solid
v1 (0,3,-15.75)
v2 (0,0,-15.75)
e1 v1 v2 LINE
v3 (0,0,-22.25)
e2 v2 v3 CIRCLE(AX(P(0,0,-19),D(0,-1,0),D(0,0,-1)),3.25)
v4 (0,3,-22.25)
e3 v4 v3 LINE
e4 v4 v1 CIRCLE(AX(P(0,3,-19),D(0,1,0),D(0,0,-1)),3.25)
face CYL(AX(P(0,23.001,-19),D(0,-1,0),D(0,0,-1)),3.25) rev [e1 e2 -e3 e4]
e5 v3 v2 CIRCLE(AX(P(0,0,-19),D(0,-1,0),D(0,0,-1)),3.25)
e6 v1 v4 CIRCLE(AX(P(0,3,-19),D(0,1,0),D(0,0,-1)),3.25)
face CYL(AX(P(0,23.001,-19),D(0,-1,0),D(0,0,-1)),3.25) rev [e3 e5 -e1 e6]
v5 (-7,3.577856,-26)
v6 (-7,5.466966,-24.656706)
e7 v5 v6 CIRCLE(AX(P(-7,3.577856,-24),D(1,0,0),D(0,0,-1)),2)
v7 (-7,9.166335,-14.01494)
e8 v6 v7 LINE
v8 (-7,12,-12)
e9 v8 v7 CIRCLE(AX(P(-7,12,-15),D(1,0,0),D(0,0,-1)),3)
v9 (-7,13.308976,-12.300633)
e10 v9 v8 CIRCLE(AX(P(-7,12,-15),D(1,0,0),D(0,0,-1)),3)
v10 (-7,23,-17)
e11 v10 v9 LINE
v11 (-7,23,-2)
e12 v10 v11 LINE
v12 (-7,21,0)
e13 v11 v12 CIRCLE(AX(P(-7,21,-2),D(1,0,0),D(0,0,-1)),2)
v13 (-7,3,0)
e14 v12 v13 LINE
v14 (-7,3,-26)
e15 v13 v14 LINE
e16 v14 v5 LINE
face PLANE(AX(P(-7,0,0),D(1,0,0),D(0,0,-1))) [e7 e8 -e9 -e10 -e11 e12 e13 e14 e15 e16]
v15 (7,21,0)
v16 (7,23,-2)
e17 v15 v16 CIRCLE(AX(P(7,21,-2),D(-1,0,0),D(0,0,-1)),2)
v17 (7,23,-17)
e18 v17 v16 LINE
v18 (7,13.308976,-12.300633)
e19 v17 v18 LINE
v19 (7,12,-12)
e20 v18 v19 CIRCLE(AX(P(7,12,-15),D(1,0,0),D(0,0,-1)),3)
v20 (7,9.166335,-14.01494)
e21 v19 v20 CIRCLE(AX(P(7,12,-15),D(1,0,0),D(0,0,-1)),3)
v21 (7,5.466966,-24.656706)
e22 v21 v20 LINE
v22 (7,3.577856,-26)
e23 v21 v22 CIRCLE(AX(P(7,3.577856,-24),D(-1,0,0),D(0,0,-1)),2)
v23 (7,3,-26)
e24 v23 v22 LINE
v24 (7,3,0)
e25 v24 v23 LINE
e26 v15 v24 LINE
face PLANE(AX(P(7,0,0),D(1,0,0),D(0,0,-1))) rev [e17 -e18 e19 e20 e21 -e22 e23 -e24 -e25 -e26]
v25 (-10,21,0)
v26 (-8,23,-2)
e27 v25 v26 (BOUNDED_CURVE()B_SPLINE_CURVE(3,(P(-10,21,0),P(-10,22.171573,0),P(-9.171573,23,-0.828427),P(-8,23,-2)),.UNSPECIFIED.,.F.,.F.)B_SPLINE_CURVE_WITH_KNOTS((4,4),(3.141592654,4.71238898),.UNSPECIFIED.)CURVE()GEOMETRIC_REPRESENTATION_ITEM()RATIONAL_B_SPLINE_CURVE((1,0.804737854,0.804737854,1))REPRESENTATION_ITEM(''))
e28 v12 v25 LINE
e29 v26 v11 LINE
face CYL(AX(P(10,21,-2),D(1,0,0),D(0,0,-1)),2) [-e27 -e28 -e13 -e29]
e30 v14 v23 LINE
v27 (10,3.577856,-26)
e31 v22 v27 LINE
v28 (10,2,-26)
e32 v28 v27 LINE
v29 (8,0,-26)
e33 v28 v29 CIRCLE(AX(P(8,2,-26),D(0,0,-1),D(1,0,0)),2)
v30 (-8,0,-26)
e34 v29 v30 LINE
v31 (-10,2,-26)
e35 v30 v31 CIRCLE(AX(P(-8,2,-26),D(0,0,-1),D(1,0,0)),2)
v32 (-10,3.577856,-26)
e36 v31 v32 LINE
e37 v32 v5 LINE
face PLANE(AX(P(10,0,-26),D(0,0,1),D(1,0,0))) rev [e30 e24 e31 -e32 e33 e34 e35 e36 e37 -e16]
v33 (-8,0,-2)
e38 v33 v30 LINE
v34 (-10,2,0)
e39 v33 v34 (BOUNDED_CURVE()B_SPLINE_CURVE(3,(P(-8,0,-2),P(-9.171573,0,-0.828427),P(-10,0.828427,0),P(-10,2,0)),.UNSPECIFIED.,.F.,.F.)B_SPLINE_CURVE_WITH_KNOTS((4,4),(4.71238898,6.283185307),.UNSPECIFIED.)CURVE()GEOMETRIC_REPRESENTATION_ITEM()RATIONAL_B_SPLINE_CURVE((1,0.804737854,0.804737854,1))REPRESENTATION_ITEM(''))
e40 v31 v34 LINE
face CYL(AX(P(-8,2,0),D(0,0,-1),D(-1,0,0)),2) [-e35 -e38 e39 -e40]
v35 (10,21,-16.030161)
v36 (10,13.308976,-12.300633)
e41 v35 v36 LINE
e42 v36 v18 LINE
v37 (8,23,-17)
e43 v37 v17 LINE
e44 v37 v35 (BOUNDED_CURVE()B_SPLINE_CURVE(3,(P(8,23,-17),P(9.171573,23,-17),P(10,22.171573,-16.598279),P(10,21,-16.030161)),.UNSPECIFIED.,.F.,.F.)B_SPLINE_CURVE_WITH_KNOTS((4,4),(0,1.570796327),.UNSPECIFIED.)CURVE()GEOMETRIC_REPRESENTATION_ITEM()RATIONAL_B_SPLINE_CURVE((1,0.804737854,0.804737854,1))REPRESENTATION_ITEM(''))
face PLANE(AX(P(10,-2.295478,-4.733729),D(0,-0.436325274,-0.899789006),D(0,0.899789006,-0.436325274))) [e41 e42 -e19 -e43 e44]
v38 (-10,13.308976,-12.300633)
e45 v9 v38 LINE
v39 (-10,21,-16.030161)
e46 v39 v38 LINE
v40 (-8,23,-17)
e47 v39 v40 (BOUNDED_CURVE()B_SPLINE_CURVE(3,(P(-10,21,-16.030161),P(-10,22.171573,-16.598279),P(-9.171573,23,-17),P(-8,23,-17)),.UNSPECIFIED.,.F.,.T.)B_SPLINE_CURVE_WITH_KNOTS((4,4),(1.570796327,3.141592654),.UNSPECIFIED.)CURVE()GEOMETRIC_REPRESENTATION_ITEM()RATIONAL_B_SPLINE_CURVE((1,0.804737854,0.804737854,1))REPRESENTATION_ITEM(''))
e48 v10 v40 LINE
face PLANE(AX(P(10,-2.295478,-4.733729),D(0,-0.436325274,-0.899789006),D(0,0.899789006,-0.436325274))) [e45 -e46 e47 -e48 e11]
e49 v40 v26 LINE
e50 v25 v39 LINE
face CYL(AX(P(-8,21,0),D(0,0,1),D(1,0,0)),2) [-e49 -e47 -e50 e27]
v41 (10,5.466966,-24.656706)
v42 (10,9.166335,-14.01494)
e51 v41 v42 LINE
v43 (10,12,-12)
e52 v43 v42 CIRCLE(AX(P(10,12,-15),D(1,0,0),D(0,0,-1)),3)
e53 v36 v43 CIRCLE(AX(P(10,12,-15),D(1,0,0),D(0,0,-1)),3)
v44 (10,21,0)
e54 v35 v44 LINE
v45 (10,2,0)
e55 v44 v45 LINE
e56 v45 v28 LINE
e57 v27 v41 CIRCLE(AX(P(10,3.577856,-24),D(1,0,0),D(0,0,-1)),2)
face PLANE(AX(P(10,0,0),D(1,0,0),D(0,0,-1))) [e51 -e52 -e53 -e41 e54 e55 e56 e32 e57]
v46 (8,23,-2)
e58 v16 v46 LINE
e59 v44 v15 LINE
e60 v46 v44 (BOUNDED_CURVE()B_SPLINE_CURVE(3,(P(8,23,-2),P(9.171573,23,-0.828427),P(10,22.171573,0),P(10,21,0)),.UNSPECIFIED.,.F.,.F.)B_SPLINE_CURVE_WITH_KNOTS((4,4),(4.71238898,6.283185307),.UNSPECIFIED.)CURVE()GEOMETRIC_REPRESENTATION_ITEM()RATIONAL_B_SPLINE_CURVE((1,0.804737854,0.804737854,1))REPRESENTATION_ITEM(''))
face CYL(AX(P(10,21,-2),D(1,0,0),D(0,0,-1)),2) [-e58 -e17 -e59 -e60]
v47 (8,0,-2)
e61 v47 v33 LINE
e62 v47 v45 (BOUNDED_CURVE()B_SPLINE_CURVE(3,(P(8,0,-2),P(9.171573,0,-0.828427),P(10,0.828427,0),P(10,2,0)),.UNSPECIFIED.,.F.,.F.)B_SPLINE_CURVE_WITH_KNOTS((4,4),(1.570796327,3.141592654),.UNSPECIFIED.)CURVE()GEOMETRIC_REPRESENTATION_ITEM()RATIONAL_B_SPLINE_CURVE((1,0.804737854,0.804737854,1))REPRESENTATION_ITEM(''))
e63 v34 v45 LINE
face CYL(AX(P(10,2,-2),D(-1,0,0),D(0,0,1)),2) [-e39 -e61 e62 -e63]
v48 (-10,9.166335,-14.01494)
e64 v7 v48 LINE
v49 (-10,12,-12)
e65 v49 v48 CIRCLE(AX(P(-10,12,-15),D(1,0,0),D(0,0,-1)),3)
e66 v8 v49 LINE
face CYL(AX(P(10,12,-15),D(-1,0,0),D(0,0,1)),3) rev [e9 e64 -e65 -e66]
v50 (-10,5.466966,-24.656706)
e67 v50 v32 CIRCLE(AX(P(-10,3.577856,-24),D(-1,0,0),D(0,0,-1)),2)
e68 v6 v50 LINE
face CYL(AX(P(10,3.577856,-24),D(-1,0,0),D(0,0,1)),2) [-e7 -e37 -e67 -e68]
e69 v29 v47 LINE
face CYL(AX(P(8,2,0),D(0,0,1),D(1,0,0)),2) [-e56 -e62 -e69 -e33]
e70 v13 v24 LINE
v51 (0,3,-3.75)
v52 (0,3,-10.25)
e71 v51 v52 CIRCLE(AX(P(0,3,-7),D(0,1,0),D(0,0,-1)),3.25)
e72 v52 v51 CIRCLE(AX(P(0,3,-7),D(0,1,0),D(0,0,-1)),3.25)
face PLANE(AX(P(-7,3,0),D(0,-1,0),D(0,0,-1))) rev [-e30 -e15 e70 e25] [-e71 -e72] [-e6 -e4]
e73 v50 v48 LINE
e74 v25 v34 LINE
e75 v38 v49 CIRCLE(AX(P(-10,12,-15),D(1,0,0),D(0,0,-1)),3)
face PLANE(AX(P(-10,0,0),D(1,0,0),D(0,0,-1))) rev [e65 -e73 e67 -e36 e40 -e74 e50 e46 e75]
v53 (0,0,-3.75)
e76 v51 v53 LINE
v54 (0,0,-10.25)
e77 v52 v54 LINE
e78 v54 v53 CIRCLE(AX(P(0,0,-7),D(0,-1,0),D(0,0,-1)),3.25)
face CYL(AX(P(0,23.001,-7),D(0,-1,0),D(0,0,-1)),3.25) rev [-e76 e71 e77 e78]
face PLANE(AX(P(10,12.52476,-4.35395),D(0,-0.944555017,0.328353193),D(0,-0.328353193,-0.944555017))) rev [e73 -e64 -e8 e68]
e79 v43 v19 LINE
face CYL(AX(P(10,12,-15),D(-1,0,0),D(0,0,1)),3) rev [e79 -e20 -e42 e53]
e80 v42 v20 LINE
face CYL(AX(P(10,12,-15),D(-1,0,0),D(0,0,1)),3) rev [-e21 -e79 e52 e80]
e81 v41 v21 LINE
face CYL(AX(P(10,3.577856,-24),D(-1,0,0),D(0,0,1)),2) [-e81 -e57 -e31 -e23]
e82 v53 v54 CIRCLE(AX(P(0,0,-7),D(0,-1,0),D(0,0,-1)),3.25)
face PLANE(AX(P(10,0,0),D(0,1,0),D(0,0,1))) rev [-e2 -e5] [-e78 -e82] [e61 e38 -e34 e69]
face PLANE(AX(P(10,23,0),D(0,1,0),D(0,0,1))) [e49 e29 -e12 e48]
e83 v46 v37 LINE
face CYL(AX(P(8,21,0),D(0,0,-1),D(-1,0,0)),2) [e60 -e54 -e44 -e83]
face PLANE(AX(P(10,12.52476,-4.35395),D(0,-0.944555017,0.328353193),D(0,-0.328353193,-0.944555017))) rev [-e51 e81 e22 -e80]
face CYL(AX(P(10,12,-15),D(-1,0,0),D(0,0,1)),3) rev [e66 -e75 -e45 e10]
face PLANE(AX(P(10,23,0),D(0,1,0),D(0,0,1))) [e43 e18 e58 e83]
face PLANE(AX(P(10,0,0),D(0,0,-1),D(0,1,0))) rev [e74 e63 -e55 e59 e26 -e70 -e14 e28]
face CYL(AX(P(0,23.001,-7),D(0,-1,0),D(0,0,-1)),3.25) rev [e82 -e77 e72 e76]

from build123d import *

# Parameters (mm, degrees)
EXTRUDE_1_DEPTH     = 10
SKETCH_2_W          = 26
SKETCH_2_H          = 20
CUT_EXTRUDE_1_DEPTH = 7
CUT_EXTRUDE_2_REACH = 38.125
SKETCH_3_R          = 3.25
FILLET_3_R          = 2


with BuildPart() as part:
    # 草图1 → 凸台-拉伸1 (new, symmetric)
    with BuildSketch(Plane(origin=(0, 0, 0), x_dir=(0, 0, -1), z_dir=(1, 0, 0))):
        with BuildLine():
            Line((17, 23), (0, 23))
            Line((0, 23), (0, 0))
            Line((0, 0), (26, 0))
            Line((26, 0), (26, 5))
            Line((26, 5), (14.014940421, 9.166334948))
            ThreePointArc((14.014940421, 9.166334948), (12.227975796, 10.852881082), (12.300632982, 13.308975821))
            Line((12.300632982, 13.308975821), (17, 23))
        make_face()
    extrude(amount=EXTRUDE_1_DEPTH, both=True)

    # 草图2 → 切除-拉伸1 (cut, symmetric)
    with BuildSketch(Plane(origin=(0, 0, 0), x_dir=(0, 0, -1), z_dir=(1, 0, 0))):
        with Locations((13, 13)):
            Rectangle(SKETCH_2_W, SKETCH_2_H)
    extrude(amount=CUT_EXTRUDE_1_DEPTH, both=True, mode=Mode.SUBTRACT)

    # 草图3 → 切除-拉伸2 (cut, up to next)
    with BuildSketch(Plane.XZ, mode=Mode.PRIVATE) as cut_extrude_2_sk1:
        with Locations(Location((0, -7, 0), (0, 0, 270))):
            Circle(SKETCH_3_R)
    cut_extrude_2_tool1 = extrude(cut_extrude_2_sk1.sketch, amount=-CUT_EXTRUDE_2_REACH, mode=Mode.PRIVATE) & part.part
    # 草图3 → 切除-拉伸2 (cut, up to next)
    with BuildSketch(Plane.XZ, mode=Mode.PRIVATE) as cut_extrude_2_sk2:
        with Locations(Location((0, -19, 0), (0, 0, 270))):
            Circle(SKETCH_3_R)
    cut_extrude_2_tool2 = extrude(cut_extrude_2_sk2.sketch, amount=-CUT_EXTRUDE_2_REACH, mode=Mode.PRIVATE) & part.part
    add(cut_extrude_2_tool1.solids().sort_by_distance((0, 0, -7))[0], mode=Mode.SUBTRACT)
    add(cut_extrude_2_tool2.solids().sort_by_distance((0, 0, -19))[0], mode=Mode.SUBTRACT)

    # 圆角3
    fillet_3_edges = [part.edges().sort_by_distance(p)[0] for p in [
        (-10, 23, -8.5),
        (10, 23, -8.5),
        (8.5, 5, -26),
        (0, 0, 0),
        (8.5, 23, 0),
        (10, 0, -13),
        (-8.5, 5, -26),
        (-8.5, 23, 0),
        (-10, 0, -13),
    ]]
    fillet(fillet_3_edges, radius=FILLET_3_R)


solid = part.part
